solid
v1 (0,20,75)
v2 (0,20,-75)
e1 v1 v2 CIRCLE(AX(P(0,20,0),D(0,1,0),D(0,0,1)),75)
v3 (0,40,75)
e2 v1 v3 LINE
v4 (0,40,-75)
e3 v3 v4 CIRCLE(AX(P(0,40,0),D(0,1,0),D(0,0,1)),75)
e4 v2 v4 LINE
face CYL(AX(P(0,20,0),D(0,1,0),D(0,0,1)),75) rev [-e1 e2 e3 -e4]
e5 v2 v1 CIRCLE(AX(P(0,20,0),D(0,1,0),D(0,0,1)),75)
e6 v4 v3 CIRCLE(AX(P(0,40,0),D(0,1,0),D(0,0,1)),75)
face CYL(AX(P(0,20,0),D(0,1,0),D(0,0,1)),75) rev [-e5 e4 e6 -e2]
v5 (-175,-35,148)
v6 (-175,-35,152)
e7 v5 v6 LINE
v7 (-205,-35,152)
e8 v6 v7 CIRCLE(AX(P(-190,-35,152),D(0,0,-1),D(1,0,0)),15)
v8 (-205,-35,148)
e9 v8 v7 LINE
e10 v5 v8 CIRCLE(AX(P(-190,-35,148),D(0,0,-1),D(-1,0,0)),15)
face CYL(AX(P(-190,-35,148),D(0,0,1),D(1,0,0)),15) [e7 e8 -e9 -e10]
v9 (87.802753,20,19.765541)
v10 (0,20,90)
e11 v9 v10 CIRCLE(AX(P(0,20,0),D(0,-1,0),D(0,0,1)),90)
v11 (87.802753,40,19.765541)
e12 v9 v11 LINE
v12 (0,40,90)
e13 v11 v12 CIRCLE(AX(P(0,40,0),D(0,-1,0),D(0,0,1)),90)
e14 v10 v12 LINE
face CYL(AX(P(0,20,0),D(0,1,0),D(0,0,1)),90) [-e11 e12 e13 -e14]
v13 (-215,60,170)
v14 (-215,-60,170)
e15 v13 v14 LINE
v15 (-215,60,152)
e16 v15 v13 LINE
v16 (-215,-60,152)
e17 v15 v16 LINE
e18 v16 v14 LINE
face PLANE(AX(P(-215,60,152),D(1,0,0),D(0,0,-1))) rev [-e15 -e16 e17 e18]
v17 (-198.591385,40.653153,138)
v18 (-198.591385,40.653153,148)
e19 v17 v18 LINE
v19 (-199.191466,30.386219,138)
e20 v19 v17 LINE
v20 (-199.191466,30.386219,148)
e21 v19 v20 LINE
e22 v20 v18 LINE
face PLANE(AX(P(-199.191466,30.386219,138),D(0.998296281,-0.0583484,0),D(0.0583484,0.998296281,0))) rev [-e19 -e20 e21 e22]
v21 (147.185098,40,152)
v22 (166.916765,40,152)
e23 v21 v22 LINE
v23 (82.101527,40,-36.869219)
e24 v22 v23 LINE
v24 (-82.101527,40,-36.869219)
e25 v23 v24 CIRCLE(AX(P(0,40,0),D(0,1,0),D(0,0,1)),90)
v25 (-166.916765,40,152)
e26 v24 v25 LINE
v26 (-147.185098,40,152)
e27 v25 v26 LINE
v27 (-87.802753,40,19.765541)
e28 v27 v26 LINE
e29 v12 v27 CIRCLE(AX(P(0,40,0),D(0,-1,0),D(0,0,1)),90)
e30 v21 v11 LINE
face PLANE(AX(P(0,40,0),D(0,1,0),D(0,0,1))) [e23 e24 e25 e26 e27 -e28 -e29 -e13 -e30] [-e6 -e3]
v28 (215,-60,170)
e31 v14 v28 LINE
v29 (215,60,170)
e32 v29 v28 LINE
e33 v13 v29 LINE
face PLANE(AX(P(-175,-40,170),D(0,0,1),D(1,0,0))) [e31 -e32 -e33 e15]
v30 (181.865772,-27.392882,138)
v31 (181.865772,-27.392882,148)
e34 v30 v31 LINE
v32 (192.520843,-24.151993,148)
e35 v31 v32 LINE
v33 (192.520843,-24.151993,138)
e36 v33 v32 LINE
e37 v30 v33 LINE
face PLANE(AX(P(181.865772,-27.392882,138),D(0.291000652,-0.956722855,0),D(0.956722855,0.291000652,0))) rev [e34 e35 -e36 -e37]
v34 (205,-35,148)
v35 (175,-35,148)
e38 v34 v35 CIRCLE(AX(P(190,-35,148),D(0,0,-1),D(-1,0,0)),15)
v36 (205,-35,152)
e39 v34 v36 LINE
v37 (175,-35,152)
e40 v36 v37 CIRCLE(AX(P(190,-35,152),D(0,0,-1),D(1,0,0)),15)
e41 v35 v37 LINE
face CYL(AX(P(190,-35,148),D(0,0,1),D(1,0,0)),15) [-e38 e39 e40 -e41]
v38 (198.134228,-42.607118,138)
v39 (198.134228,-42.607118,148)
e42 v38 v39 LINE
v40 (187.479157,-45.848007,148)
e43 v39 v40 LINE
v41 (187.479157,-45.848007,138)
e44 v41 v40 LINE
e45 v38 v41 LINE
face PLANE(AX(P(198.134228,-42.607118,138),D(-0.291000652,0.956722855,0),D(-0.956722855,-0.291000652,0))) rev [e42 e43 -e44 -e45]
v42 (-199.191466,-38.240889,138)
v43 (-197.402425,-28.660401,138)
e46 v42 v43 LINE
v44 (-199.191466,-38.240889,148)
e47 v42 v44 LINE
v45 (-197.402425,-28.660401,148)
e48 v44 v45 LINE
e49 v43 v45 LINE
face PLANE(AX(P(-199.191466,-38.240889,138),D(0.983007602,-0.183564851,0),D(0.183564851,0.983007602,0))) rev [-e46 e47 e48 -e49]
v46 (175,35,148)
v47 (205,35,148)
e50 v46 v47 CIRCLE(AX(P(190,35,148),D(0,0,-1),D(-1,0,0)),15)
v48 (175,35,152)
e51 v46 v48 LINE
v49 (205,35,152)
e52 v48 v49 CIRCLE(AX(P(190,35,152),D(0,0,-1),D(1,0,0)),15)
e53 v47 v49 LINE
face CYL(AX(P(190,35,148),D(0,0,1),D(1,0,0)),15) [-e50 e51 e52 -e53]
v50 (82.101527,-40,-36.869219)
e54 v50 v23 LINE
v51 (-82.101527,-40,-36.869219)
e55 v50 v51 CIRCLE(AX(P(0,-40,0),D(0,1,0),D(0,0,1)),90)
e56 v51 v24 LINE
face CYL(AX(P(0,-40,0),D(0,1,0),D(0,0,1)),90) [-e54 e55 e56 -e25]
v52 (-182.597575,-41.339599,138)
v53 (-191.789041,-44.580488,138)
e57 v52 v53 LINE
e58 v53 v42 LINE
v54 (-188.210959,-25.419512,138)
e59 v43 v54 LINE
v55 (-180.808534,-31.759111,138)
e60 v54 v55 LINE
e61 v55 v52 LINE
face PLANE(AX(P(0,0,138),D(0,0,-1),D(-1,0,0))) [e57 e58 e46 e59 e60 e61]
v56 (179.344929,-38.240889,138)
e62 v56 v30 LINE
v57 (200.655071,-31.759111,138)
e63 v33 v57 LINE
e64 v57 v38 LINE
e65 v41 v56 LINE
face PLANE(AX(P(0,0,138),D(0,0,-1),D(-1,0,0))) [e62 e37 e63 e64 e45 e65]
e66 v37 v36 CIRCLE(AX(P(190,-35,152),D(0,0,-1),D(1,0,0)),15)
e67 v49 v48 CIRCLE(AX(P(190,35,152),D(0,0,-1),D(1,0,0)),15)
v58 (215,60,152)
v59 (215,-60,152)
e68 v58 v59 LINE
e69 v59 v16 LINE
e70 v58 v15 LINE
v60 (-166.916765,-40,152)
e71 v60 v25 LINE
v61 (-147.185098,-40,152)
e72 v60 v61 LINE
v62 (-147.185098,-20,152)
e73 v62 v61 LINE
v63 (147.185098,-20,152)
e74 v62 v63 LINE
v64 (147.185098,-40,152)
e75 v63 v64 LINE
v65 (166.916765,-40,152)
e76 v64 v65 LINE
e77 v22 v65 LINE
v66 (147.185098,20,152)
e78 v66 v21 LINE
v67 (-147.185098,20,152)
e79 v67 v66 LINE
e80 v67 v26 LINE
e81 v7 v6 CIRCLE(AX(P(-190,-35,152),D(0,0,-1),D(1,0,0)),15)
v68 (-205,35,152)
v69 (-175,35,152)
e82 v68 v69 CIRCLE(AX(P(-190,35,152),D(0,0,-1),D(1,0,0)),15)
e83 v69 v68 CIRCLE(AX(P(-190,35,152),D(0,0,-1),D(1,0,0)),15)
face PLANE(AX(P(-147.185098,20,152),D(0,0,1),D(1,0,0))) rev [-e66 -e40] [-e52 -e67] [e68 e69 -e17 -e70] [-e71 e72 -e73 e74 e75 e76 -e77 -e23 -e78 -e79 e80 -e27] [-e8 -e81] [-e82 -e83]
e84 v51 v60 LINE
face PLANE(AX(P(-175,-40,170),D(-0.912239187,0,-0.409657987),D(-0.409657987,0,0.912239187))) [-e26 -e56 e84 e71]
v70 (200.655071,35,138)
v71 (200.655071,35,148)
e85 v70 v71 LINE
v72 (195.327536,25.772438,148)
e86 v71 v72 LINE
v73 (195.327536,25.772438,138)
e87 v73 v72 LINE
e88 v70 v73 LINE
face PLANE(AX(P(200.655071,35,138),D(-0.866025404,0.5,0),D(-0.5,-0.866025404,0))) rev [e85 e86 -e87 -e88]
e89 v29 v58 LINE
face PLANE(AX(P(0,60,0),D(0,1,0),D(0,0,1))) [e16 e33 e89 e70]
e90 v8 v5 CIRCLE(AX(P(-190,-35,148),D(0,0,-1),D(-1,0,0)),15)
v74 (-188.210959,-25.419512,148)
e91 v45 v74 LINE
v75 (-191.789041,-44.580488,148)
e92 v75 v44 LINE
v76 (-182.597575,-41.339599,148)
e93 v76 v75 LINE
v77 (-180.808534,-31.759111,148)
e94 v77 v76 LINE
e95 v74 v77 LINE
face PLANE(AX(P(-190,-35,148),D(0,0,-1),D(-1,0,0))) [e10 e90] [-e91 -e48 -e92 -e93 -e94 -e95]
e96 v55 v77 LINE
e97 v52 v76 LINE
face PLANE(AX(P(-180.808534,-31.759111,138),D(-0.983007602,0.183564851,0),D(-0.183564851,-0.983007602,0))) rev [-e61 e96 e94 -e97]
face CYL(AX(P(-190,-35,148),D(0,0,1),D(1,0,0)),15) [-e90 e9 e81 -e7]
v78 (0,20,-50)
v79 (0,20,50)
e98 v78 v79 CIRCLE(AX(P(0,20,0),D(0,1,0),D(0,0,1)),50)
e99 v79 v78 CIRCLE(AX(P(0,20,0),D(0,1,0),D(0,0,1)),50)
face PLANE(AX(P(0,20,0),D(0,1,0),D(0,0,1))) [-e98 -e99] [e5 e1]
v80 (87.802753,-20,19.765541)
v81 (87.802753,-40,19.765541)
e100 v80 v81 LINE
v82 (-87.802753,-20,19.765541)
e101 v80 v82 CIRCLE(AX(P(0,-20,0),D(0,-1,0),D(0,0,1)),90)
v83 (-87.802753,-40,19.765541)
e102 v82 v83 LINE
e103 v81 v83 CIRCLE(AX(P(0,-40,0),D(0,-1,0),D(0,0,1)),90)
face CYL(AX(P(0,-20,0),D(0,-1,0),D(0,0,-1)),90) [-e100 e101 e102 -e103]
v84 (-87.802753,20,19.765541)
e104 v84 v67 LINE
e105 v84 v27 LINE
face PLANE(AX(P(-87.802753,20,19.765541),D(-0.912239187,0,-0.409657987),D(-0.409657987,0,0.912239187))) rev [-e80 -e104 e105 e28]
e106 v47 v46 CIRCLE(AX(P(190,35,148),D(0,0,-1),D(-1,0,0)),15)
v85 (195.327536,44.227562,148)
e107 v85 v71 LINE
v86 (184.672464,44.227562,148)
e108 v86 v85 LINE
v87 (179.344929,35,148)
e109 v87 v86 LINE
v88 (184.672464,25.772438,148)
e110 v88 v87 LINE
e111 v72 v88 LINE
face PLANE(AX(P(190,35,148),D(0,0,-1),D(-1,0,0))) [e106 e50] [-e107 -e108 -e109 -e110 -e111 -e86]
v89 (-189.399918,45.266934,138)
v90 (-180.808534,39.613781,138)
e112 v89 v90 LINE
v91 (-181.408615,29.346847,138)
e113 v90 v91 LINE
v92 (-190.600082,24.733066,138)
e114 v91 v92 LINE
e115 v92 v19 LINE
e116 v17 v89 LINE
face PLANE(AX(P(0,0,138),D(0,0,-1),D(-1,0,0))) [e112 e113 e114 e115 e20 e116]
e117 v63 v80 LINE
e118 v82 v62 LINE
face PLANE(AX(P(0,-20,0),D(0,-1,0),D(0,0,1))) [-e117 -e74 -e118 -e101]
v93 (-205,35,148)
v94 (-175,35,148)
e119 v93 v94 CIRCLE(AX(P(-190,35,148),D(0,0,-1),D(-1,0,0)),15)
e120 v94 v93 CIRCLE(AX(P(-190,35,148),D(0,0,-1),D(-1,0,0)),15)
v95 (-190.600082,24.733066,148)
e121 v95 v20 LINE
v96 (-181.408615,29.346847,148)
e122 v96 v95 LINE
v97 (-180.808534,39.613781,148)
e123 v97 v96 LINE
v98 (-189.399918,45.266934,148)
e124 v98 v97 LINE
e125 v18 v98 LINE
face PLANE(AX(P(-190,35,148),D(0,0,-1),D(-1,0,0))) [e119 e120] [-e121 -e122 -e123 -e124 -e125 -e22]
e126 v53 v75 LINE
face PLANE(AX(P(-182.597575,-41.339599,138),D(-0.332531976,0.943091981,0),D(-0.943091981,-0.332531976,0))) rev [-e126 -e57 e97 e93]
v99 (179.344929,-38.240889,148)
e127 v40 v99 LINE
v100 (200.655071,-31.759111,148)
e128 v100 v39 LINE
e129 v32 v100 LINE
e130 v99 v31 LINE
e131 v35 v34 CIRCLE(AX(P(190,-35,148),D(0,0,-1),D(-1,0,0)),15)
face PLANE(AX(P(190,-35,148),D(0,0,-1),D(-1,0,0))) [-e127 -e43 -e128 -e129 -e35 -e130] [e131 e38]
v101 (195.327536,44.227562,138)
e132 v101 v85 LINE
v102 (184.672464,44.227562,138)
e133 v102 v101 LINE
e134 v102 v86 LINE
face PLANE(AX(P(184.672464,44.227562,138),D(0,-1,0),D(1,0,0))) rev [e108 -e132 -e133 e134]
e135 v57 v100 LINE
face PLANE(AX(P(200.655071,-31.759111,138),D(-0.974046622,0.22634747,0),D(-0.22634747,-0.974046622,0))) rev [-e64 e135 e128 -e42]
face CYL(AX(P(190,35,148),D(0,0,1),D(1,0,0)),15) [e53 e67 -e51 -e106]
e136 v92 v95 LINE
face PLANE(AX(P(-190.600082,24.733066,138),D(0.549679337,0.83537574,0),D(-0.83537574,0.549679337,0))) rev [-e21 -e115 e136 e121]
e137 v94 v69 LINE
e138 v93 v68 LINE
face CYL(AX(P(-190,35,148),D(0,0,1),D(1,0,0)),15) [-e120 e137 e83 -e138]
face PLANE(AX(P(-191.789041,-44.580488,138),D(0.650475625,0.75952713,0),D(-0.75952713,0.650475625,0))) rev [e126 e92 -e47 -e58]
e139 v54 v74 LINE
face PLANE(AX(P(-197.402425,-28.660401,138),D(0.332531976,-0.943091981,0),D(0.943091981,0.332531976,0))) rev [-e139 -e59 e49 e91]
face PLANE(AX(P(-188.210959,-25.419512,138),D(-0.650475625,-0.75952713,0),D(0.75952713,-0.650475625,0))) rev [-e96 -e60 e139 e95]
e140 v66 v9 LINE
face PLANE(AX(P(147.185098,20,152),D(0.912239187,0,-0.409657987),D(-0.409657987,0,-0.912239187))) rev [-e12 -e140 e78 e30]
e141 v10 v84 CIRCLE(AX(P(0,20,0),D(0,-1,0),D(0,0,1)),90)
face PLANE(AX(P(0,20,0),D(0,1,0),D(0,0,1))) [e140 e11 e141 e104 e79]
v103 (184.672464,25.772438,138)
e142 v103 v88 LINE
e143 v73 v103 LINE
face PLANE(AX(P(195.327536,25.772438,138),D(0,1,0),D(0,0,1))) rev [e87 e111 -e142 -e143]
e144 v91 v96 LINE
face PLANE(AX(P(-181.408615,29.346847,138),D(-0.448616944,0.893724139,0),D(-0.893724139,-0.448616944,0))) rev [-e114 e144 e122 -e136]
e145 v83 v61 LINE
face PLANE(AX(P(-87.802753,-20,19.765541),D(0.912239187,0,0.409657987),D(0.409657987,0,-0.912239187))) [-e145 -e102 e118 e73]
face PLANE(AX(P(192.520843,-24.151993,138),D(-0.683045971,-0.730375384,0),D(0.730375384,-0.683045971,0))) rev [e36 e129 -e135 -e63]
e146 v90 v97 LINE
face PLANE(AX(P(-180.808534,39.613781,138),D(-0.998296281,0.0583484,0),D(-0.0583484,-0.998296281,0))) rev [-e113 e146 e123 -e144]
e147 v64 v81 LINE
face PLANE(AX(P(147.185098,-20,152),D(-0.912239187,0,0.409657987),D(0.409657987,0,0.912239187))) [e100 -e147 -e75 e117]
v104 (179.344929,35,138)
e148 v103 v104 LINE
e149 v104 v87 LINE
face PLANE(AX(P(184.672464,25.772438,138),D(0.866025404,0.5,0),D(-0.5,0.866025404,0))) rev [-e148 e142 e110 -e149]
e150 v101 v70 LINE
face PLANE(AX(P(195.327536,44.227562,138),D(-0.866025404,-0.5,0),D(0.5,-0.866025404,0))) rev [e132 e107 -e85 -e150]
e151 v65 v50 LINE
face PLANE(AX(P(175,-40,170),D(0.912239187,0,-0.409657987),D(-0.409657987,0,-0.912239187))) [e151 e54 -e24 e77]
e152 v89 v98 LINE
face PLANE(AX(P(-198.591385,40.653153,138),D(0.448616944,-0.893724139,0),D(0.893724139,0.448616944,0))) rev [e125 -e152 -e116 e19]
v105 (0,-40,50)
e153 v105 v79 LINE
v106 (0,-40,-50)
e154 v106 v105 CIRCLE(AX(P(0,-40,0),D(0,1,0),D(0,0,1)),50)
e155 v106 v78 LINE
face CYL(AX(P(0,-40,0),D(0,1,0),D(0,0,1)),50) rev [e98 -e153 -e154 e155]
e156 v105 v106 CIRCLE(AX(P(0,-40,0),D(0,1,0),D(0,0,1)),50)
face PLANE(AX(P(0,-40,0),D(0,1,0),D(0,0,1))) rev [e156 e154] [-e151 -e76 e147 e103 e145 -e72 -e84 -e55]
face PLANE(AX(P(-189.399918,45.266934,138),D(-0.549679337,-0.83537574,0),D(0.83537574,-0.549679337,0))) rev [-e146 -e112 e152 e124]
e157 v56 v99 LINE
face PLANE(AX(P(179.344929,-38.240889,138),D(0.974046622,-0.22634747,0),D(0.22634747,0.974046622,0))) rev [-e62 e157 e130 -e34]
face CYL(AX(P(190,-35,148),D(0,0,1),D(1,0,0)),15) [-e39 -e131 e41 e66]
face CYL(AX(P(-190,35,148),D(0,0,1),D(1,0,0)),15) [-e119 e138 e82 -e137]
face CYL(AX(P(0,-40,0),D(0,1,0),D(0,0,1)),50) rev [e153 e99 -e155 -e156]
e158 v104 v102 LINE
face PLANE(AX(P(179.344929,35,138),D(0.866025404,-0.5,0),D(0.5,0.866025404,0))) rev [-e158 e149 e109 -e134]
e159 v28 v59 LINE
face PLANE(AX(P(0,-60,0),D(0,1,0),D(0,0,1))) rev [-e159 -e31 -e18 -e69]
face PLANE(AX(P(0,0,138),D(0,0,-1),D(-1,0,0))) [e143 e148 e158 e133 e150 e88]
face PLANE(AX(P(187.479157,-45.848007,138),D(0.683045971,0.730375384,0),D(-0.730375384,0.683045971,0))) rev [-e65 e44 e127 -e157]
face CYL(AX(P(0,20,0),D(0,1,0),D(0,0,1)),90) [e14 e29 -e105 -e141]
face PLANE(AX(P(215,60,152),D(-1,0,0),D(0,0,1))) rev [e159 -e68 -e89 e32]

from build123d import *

# Parameters (mm, degrees)
BOSS_EXTRUDE1_DEPTH      = 40
BOSS_EXTRUDE1_DEPTH_BACK = 40
SKETCH1_R                = 50
CUT_EXTRUDE1_START       = -20
SKETCH2_R                = 75
SKETCH2_R_2              = 50
CUT_EXTRUDE1_DEPTH       = 20
CUT_EXTRUDE2_START       = -20
CUT_EXTRUDE2_DEPTH       = 20
BOSS_EXTRUDE2_DEPTH      = 20
BOSS_EXTRUDE2_DEPTH_BACK = 100
SKETCH4_W                = 430
SKETCH4_H                = 18
SKETCH5_R                = 15
BOSS_EXTRUDE3_DEPTH      = 4
BOSS_EXTRUDE4_DEPTH      = 10


with BuildPart() as part:
    # Sketch1 → Boss-Extrude1 (new, two sides: drawn at the far end of the back side and taken through both)
    with BuildSketch(Plane(origin=(0, 0, 0), x_dir=(1, 0, 0), z_dir=(0, 1, 0)).offset(-BOSS_EXTRUDE1_DEPTH_BACK)):
        with BuildLine():
            Line((-175, -170), (175, -170))
            Line((175, -170), (82.10152682, 36.869218785))
            ThreePointArc((82.10152682, 36.869218785), (0, 90), (-82.10152682, 36.869218785))
            Line((-82.10152682, 36.869218785), (-175, -170))
        make_face()
        with Locations(Location((0, 0, 0), (0, 0, 270))):
            Circle(SKETCH1_R, mode=Mode.SUBTRACT)
    extrude(amount=BOSS_EXTRUDE1_DEPTH + BOSS_EXTRUDE1_DEPTH_BACK)

    # Sketch2 → Cut-Extrude1 (cut)
    with BuildSketch(Plane(origin=(0, 40, 0), x_dir=(1, 0, 0), z_dir=(0, 1, 0)).offset(CUT_EXTRUDE1_START)):
        with Locations(Location((0, 0, 0), (0, 0, 270))):
            Circle(SKETCH2_R)
        with Locations(Location((0, 0, 0), (0, 0, 270))):
            Circle(SKETCH2_R_2, mode=Mode.SUBTRACT)
    extrude(amount=CUT_EXTRUDE1_DEPTH, mode=Mode.SUBTRACT)

    # Sketch3 → Cut-Extrude2 (cut)
    with BuildSketch(Plane(origin=(0, 40, 0), x_dir=(1, 0, 0), z_dir=(0, 1, 0)).offset(CUT_EXTRUDE2_START)):
        with BuildLine():
            Line((-87.802752727, -19.765541064), (-147.18509781, -152))
            Line((-147.18509781, -152), (147.18509781, -152))
            Line((147.18509781, -152), (87.802752727, -19.765541064))
            ThreePointArc((87.802752727, -19.765541064), (0, -90), (-87.802752727, -19.765541064))
        make_face()
    cut_extrude2 = extrude(amount=CUT_EXTRUDE2_DEPTH, mode=Mode.SUBTRACT)

    # Mirror1: Cut-Extrude2 across plane
    add(cut_extrude2.mirror(Plane.ZX), mode=Mode.SUBTRACT)

    # Sketch4 → Boss-Extrude2 (add, two sides: drawn at the far end of the back side and taken through both)
    with BuildSketch(Plane(origin=(0, 40, 0), x_dir=(1, 0, 0), z_dir=(0, 1, 0)).offset(-BOSS_EXTRUDE2_DEPTH_BACK)):
        with Locations((0, -161)):
            Rectangle(SKETCH4_W, SKETCH4_H)
    extrude(amount=BOSS_EXTRUDE2_DEPTH + BOSS_EXTRUDE2_DEPTH_BACK)

    # Sketch5 → Boss-Extrude3 (add)
    with BuildSketch(Plane(origin=(0, 0, 152), x_dir=(-1, 0, 0), z_dir=(0, 0, -1))):
        with Locations(Location((-190, 35, 0), (0, 0, 180))):
            Circle(SKETCH5_R)
        with Locations(Location((-190, -35, 0), (0, 0, 180))):
            Circle(SKETCH5_R)
        with Locations(Location((190, -35, 0), (0, 0, 180))):
            Circle(SKETCH5_R)
        with Locations(Location((190, 35, 0), (0, 0, 180))):
            Circle(SKETCH5_R)
    extrude(amount=BOSS_EXTRUDE3_DEPTH)

    # Sketch6 → Boss-Extrude4 (add)
    with BuildSketch(Plane(origin=(0, 0, 148), x_dir=(-1, 0, 0), z_dir=(0, 0, -1))):
        Polygon((-179.344928978, 35), (-184.672464489, 44.227562184), (-195.327535511, 44.227562184), (-200.655071022, 35), (-195.327535511, 25.772437816), (-184.672464489, 25.772437816), align=None)
        Polygon((-179.344928978, -38.24088904), (-181.86577225, -27.392882336), (-192.520843272, -24.151993296), (-200.655071022, -31.75911096), (-198.13422775, -42.607117664), (-187.479156728, -45.848006704), align=None)
        Polygon((199.191466328, 30.386218908), (198.591384797, 40.653152792), (189.399918469, 45.266933884), (180.808533672, 39.613781092), (181.408615203, 29.346847208), (190.600081531, 24.733066116), align=None)
        Polygon((199.191466328, -38.24088904), (197.402425403, -28.660401182), (188.210959075, -25.419512142), (180.808533672, -31.75911096), (182.597574597, -41.339598818), (191.789040925, -44.580487858), align=None)
    extrude(amount=BOSS_EXTRUDE4_DEPTH)


solid = part.part
